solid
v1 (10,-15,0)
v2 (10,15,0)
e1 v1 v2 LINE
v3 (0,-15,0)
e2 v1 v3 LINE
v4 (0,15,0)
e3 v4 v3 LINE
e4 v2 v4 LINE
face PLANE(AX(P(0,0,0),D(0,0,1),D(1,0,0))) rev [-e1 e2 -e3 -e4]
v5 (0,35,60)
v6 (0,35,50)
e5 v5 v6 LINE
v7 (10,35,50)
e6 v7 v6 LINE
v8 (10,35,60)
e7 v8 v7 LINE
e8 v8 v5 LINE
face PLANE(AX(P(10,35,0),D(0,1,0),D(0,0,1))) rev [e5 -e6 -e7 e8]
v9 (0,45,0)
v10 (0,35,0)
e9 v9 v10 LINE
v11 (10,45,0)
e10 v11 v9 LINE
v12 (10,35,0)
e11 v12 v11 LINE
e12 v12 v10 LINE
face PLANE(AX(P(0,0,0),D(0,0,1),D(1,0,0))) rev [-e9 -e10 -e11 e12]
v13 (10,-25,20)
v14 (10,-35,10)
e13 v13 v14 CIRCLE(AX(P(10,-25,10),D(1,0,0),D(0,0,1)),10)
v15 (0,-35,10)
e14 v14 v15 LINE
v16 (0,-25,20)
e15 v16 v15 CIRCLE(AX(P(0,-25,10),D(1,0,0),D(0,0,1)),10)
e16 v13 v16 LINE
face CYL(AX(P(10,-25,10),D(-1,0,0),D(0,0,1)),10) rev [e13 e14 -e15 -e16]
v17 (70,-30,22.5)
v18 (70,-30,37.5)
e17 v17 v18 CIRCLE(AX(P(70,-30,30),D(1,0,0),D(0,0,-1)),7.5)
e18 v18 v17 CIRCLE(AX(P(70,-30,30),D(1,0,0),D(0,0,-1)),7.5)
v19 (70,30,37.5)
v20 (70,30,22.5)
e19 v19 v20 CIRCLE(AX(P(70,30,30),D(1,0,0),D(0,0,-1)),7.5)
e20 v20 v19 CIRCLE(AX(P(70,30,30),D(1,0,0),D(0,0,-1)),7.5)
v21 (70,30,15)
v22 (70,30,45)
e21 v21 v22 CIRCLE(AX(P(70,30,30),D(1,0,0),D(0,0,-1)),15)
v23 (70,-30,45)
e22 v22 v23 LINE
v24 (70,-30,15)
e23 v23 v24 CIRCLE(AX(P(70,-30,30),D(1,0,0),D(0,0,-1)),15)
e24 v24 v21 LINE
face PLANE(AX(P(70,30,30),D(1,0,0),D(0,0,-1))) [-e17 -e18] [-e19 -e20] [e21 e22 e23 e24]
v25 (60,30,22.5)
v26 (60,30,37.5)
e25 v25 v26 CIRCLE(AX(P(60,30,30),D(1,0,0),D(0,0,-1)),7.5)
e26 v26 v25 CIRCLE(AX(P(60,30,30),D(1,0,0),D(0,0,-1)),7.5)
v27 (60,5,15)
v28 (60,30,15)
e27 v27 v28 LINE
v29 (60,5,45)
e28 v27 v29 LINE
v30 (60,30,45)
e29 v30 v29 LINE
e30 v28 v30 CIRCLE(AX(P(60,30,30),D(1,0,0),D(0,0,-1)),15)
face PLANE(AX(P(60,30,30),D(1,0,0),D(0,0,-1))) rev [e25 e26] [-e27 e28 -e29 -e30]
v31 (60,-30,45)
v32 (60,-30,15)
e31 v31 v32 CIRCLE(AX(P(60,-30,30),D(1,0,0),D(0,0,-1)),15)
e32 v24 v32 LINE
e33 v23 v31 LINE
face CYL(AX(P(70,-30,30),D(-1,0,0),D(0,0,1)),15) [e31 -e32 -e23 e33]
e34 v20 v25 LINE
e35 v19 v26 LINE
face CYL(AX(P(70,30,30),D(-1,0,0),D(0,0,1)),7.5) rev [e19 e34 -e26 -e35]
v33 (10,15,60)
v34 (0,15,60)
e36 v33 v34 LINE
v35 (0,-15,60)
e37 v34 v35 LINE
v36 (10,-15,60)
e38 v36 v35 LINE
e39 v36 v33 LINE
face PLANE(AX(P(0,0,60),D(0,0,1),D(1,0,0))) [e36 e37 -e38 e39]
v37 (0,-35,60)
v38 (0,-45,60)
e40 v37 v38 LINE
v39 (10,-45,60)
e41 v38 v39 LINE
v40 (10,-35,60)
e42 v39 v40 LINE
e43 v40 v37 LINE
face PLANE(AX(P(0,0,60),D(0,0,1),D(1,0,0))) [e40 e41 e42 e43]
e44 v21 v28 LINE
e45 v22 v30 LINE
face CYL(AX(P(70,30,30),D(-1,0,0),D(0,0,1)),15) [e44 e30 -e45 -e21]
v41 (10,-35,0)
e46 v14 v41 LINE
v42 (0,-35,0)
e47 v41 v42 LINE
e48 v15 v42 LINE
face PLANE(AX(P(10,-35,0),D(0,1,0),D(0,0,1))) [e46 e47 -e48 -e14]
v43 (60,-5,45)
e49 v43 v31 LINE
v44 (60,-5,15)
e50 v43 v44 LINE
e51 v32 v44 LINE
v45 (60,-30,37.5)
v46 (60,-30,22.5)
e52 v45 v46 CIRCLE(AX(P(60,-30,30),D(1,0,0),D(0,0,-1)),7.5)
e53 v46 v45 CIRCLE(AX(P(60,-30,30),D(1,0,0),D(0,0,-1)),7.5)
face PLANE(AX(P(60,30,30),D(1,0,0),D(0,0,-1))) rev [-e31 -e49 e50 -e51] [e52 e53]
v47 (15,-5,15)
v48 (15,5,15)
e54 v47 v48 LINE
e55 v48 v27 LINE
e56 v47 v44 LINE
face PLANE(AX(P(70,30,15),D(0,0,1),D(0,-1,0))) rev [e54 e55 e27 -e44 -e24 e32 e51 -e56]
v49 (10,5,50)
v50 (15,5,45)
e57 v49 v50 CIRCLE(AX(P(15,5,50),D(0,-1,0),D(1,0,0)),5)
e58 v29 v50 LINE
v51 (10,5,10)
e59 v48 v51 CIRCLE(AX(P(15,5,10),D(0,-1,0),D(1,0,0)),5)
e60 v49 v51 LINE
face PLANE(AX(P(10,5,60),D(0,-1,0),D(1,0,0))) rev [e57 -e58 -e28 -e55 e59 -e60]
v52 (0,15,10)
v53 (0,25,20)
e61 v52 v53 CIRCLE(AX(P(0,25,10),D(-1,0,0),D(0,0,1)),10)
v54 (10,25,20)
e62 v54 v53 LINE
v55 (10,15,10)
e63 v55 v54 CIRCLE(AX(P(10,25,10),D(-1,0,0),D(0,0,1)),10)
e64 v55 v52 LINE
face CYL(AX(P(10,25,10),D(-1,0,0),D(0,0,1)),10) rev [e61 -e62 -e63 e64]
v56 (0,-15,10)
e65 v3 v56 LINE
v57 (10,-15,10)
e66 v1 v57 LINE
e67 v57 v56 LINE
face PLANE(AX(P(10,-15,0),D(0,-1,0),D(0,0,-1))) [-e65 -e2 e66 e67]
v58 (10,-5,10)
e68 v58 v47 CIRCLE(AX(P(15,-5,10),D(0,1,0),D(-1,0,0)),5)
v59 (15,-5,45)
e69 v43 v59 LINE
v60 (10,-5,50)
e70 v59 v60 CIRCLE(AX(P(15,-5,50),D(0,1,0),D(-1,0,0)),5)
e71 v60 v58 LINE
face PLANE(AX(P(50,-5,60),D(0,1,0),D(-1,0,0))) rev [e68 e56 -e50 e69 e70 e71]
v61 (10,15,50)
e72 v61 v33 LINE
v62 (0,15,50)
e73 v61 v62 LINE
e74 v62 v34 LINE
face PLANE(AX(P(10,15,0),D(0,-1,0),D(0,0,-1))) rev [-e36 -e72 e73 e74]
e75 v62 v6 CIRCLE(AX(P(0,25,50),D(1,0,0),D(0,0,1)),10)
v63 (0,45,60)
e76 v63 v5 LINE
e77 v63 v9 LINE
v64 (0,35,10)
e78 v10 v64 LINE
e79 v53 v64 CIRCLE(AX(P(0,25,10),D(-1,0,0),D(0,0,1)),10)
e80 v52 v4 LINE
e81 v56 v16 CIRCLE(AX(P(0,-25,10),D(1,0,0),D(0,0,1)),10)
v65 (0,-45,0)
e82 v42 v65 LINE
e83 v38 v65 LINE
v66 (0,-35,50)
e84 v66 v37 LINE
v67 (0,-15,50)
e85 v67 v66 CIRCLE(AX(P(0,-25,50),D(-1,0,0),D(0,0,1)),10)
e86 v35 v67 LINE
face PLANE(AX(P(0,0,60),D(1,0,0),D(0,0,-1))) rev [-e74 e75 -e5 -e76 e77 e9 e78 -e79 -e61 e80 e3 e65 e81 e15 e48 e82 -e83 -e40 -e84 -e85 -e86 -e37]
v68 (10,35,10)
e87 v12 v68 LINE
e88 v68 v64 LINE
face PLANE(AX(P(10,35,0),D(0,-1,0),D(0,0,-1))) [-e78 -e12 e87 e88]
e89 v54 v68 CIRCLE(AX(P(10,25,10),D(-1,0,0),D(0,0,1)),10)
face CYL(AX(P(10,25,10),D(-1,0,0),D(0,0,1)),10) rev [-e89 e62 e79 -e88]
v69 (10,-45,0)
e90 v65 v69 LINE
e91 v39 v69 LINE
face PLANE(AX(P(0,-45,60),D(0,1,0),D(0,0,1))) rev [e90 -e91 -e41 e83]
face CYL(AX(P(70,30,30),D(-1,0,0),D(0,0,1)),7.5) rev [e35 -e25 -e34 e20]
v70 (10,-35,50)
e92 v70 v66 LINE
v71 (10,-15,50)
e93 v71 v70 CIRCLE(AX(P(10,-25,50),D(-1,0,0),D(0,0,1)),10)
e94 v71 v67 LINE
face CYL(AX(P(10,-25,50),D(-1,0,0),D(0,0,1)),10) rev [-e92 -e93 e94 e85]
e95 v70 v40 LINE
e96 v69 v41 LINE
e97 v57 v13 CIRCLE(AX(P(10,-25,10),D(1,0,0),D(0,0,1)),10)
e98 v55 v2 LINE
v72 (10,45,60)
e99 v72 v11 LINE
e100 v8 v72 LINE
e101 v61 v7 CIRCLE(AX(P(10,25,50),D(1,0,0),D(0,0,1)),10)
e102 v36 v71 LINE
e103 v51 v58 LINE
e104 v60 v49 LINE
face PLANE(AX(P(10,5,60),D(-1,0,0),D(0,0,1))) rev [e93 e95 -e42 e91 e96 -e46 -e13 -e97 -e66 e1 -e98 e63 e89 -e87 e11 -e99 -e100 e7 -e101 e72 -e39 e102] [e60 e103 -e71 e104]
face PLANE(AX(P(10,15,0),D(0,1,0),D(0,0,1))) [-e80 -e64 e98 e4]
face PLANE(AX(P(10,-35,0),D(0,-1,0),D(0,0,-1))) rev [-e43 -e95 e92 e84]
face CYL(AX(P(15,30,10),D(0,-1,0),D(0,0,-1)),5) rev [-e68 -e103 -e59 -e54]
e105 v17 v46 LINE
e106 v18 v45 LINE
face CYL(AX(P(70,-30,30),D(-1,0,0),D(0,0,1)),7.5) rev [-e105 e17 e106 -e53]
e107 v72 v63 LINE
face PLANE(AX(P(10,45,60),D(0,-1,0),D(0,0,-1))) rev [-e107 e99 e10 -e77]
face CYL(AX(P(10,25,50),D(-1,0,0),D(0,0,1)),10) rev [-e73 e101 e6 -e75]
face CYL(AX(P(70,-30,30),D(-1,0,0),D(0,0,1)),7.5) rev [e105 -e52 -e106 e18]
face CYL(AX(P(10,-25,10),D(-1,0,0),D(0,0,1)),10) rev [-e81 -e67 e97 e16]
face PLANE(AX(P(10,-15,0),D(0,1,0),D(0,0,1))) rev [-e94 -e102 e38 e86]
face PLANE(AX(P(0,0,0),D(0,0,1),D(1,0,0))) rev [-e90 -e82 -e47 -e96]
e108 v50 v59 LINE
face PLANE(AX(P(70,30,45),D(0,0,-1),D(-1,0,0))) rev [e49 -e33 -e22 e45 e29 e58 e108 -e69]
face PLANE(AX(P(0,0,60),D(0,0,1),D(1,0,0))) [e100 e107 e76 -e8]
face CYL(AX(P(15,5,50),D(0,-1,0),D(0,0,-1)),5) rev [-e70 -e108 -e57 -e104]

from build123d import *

# Parameters (mm, degrees)
H_BODY_EXTRUDE_60_DEPTH   = 60
RELIEF_CUT_10_DEPTH       = 10
CONNECTOR_ARM_SKETCH_R    = 7.5
CONNECTOR_ARM_BOSS_DEPTH  = 10
NOTCH_CUT_A_SKETCH_W      = 60
NOTCH_CUT_A_SKETCH_H      = 40
NOTCH_CUT_A_DEPTH         = 10
NOTCH_CUT_B_SKETCH_W      = 60
NOTCH_CUT_B_SKETCH_H      = 40
NOTCH_CUT_B_DEPTH         = 10
LINK_PLATE_SKETCH_R       = 7.5
LINK_PLATE_BOSS_DEPTH     = 10
LINK_PLATE_HOLES_SKETCH_W = 50
LINK_PLATE_HOLES_SKETCH_H = 15
LINK_PLATE_HOLES_DEPTH    = 105.880884817
EDGE_FILLETS_R5_R         = 5


with BuildPart() as part:
    # H Profile Sketch → H Body Extrude 60 (new body)
    with BuildSketch(Plane.XY):
        Polygon((0, 0), (0, 45), (10, 45), (10, 5), (50, 5), (50, 45), (60, 45), (60, -45), (50, -45), (50, -5), (10, -5), (10, -45), (0, -45), align=None)
    extrude(amount=H_BODY_EXTRUDE_60_DEPTH)

    # Relief Cut Sketch → Relief Cut 10 (cut)
    with BuildSketch(Plane.ZY):
        with BuildLine():
            Line((10, 35), (0, 35))
            Line((0, 35), (0, 15))
            Line((0, 15), (10, 15))
            ThreePointArc((10, 15), (20, 25), (10, 35))
        make_face()
        with BuildLine():
            Line((60, 15), (60, 35))
            Line((60, 35), (50, 35))
            ThreePointArc((50, 35), (40, 25), (50, 15))
            Line((50, 15), (60, 15))
        make_face()
        with BuildLine():
            Line((10, -15), (0, -15))
            Line((0, -15), (0, -35))
            Line((0, -35), (10, -35))
            ThreePointArc((10, -35), (20, -25), (10, -15))
        make_face()
        with BuildLine():
            Line((60, -35), (60, -15))
            Line((60, -15), (50, -15))
            ThreePointArc((50, -15), (40, -25), (50, -35))
            Line((50, -35), (60, -35))
        make_face()
    extrude(amount=-RELIEF_CUT_10_DEPTH, mode=Mode.SUBTRACT)

    # Connector Arm Sketch → Connector Arm Boss (add)
    with BuildSketch(Plane(origin=(60, 0, 0), x_dir=(0, 0, -1), z_dir=(1, 0, 0))):
        with BuildLine():
            Line((-15, 30), (-15, -30))
            ThreePointArc((-15, -30), (-30, -45), (-45, -30))
            Line((-45, -30), (-45, 30))
            ThreePointArc((-45, 30), (-30, 45), (-15, 30))
        make_face()
        with Locations((-30, 30)):
            Circle(CONNECTOR_ARM_SKETCH_R, mode=Mode.SUBTRACT)
        with Locations((-30, -30)):
            Circle(CONNECTOR_ARM_SKETCH_R, mode=Mode.SUBTRACT)
    extrude(amount=-CONNECTOR_ARM_BOSS_DEPTH)

    # Notch Cut A Sketch → Notch Cut A (cut)
    with BuildSketch(Plane.ZY.offset(-50)):
        with Locations((30, 25)):
            Rectangle(NOTCH_CUT_A_SKETCH_W, NOTCH_CUT_A_SKETCH_H)
    extrude(amount=-NOTCH_CUT_A_DEPTH, mode=Mode.SUBTRACT)

    # Notch Cut B Sketch → Notch Cut B (cut)
    with BuildSketch(Plane.ZY.offset(-50)):
        with Locations((30, -25)):
            Rectangle(NOTCH_CUT_B_SKETCH_W, NOTCH_CUT_B_SKETCH_H)
    extrude(amount=-NOTCH_CUT_B_DEPTH, mode=Mode.SUBTRACT)

    # Link Plate Sketch → Link Plate Boss (add)
    with BuildSketch(Plane(origin=(60, 0, 0), x_dir=(0, 0, -1), z_dir=(1, 0, 0))):
        with BuildLine():
            Line((-15, 30), (-15, -30))
            ThreePointArc((-15, -30), (-30, -45), (-45, -30))
            Line((-45, -30), (-45, 30))
            ThreePointArc((-45, 30), (-30, 45), (-15, 30))
        make_face()
        with Locations((-30, 30)):
            Circle(LINK_PLATE_SKETCH_R, mode=Mode.SUBTRACT)
        with Locations((-30, -30)):
            Circle(LINK_PLATE_SKETCH_R, mode=Mode.SUBTRACT)
    extrude(amount=LINK_PLATE_BOSS_DEPTH)

    # Link Plate Holes Sketch → Link Plate Holes (cut, through all)
    with BuildSketch(Plane(origin=(0, 5, 0), x_dir=(1, 0, 0), z_dir=(0, 1, 0))):
        with Locations((35, -7.5)):
            Rectangle(LINK_PLATE_HOLES_SKETCH_W, LINK_PLATE_HOLES_SKETCH_H)
        with Locations((35, -52.5)):
            Rectangle(LINK_PLATE_HOLES_SKETCH_W, LINK_PLATE_HOLES_SKETCH_H)
    extrude(amount=-LINK_PLATE_HOLES_DEPTH, mode=Mode.SUBTRACT)

    # Edge Fillets R5
    edge_fillets_r5_edges = [part.edges().sort_by_distance(p)[0] for p in [
        (10, 0, 15),
        (10, 0, 45),
    ]]
    fillet(edge_fillets_r5_edges, radius=EDGE_FILLETS_R5_R)


solid = part.part
